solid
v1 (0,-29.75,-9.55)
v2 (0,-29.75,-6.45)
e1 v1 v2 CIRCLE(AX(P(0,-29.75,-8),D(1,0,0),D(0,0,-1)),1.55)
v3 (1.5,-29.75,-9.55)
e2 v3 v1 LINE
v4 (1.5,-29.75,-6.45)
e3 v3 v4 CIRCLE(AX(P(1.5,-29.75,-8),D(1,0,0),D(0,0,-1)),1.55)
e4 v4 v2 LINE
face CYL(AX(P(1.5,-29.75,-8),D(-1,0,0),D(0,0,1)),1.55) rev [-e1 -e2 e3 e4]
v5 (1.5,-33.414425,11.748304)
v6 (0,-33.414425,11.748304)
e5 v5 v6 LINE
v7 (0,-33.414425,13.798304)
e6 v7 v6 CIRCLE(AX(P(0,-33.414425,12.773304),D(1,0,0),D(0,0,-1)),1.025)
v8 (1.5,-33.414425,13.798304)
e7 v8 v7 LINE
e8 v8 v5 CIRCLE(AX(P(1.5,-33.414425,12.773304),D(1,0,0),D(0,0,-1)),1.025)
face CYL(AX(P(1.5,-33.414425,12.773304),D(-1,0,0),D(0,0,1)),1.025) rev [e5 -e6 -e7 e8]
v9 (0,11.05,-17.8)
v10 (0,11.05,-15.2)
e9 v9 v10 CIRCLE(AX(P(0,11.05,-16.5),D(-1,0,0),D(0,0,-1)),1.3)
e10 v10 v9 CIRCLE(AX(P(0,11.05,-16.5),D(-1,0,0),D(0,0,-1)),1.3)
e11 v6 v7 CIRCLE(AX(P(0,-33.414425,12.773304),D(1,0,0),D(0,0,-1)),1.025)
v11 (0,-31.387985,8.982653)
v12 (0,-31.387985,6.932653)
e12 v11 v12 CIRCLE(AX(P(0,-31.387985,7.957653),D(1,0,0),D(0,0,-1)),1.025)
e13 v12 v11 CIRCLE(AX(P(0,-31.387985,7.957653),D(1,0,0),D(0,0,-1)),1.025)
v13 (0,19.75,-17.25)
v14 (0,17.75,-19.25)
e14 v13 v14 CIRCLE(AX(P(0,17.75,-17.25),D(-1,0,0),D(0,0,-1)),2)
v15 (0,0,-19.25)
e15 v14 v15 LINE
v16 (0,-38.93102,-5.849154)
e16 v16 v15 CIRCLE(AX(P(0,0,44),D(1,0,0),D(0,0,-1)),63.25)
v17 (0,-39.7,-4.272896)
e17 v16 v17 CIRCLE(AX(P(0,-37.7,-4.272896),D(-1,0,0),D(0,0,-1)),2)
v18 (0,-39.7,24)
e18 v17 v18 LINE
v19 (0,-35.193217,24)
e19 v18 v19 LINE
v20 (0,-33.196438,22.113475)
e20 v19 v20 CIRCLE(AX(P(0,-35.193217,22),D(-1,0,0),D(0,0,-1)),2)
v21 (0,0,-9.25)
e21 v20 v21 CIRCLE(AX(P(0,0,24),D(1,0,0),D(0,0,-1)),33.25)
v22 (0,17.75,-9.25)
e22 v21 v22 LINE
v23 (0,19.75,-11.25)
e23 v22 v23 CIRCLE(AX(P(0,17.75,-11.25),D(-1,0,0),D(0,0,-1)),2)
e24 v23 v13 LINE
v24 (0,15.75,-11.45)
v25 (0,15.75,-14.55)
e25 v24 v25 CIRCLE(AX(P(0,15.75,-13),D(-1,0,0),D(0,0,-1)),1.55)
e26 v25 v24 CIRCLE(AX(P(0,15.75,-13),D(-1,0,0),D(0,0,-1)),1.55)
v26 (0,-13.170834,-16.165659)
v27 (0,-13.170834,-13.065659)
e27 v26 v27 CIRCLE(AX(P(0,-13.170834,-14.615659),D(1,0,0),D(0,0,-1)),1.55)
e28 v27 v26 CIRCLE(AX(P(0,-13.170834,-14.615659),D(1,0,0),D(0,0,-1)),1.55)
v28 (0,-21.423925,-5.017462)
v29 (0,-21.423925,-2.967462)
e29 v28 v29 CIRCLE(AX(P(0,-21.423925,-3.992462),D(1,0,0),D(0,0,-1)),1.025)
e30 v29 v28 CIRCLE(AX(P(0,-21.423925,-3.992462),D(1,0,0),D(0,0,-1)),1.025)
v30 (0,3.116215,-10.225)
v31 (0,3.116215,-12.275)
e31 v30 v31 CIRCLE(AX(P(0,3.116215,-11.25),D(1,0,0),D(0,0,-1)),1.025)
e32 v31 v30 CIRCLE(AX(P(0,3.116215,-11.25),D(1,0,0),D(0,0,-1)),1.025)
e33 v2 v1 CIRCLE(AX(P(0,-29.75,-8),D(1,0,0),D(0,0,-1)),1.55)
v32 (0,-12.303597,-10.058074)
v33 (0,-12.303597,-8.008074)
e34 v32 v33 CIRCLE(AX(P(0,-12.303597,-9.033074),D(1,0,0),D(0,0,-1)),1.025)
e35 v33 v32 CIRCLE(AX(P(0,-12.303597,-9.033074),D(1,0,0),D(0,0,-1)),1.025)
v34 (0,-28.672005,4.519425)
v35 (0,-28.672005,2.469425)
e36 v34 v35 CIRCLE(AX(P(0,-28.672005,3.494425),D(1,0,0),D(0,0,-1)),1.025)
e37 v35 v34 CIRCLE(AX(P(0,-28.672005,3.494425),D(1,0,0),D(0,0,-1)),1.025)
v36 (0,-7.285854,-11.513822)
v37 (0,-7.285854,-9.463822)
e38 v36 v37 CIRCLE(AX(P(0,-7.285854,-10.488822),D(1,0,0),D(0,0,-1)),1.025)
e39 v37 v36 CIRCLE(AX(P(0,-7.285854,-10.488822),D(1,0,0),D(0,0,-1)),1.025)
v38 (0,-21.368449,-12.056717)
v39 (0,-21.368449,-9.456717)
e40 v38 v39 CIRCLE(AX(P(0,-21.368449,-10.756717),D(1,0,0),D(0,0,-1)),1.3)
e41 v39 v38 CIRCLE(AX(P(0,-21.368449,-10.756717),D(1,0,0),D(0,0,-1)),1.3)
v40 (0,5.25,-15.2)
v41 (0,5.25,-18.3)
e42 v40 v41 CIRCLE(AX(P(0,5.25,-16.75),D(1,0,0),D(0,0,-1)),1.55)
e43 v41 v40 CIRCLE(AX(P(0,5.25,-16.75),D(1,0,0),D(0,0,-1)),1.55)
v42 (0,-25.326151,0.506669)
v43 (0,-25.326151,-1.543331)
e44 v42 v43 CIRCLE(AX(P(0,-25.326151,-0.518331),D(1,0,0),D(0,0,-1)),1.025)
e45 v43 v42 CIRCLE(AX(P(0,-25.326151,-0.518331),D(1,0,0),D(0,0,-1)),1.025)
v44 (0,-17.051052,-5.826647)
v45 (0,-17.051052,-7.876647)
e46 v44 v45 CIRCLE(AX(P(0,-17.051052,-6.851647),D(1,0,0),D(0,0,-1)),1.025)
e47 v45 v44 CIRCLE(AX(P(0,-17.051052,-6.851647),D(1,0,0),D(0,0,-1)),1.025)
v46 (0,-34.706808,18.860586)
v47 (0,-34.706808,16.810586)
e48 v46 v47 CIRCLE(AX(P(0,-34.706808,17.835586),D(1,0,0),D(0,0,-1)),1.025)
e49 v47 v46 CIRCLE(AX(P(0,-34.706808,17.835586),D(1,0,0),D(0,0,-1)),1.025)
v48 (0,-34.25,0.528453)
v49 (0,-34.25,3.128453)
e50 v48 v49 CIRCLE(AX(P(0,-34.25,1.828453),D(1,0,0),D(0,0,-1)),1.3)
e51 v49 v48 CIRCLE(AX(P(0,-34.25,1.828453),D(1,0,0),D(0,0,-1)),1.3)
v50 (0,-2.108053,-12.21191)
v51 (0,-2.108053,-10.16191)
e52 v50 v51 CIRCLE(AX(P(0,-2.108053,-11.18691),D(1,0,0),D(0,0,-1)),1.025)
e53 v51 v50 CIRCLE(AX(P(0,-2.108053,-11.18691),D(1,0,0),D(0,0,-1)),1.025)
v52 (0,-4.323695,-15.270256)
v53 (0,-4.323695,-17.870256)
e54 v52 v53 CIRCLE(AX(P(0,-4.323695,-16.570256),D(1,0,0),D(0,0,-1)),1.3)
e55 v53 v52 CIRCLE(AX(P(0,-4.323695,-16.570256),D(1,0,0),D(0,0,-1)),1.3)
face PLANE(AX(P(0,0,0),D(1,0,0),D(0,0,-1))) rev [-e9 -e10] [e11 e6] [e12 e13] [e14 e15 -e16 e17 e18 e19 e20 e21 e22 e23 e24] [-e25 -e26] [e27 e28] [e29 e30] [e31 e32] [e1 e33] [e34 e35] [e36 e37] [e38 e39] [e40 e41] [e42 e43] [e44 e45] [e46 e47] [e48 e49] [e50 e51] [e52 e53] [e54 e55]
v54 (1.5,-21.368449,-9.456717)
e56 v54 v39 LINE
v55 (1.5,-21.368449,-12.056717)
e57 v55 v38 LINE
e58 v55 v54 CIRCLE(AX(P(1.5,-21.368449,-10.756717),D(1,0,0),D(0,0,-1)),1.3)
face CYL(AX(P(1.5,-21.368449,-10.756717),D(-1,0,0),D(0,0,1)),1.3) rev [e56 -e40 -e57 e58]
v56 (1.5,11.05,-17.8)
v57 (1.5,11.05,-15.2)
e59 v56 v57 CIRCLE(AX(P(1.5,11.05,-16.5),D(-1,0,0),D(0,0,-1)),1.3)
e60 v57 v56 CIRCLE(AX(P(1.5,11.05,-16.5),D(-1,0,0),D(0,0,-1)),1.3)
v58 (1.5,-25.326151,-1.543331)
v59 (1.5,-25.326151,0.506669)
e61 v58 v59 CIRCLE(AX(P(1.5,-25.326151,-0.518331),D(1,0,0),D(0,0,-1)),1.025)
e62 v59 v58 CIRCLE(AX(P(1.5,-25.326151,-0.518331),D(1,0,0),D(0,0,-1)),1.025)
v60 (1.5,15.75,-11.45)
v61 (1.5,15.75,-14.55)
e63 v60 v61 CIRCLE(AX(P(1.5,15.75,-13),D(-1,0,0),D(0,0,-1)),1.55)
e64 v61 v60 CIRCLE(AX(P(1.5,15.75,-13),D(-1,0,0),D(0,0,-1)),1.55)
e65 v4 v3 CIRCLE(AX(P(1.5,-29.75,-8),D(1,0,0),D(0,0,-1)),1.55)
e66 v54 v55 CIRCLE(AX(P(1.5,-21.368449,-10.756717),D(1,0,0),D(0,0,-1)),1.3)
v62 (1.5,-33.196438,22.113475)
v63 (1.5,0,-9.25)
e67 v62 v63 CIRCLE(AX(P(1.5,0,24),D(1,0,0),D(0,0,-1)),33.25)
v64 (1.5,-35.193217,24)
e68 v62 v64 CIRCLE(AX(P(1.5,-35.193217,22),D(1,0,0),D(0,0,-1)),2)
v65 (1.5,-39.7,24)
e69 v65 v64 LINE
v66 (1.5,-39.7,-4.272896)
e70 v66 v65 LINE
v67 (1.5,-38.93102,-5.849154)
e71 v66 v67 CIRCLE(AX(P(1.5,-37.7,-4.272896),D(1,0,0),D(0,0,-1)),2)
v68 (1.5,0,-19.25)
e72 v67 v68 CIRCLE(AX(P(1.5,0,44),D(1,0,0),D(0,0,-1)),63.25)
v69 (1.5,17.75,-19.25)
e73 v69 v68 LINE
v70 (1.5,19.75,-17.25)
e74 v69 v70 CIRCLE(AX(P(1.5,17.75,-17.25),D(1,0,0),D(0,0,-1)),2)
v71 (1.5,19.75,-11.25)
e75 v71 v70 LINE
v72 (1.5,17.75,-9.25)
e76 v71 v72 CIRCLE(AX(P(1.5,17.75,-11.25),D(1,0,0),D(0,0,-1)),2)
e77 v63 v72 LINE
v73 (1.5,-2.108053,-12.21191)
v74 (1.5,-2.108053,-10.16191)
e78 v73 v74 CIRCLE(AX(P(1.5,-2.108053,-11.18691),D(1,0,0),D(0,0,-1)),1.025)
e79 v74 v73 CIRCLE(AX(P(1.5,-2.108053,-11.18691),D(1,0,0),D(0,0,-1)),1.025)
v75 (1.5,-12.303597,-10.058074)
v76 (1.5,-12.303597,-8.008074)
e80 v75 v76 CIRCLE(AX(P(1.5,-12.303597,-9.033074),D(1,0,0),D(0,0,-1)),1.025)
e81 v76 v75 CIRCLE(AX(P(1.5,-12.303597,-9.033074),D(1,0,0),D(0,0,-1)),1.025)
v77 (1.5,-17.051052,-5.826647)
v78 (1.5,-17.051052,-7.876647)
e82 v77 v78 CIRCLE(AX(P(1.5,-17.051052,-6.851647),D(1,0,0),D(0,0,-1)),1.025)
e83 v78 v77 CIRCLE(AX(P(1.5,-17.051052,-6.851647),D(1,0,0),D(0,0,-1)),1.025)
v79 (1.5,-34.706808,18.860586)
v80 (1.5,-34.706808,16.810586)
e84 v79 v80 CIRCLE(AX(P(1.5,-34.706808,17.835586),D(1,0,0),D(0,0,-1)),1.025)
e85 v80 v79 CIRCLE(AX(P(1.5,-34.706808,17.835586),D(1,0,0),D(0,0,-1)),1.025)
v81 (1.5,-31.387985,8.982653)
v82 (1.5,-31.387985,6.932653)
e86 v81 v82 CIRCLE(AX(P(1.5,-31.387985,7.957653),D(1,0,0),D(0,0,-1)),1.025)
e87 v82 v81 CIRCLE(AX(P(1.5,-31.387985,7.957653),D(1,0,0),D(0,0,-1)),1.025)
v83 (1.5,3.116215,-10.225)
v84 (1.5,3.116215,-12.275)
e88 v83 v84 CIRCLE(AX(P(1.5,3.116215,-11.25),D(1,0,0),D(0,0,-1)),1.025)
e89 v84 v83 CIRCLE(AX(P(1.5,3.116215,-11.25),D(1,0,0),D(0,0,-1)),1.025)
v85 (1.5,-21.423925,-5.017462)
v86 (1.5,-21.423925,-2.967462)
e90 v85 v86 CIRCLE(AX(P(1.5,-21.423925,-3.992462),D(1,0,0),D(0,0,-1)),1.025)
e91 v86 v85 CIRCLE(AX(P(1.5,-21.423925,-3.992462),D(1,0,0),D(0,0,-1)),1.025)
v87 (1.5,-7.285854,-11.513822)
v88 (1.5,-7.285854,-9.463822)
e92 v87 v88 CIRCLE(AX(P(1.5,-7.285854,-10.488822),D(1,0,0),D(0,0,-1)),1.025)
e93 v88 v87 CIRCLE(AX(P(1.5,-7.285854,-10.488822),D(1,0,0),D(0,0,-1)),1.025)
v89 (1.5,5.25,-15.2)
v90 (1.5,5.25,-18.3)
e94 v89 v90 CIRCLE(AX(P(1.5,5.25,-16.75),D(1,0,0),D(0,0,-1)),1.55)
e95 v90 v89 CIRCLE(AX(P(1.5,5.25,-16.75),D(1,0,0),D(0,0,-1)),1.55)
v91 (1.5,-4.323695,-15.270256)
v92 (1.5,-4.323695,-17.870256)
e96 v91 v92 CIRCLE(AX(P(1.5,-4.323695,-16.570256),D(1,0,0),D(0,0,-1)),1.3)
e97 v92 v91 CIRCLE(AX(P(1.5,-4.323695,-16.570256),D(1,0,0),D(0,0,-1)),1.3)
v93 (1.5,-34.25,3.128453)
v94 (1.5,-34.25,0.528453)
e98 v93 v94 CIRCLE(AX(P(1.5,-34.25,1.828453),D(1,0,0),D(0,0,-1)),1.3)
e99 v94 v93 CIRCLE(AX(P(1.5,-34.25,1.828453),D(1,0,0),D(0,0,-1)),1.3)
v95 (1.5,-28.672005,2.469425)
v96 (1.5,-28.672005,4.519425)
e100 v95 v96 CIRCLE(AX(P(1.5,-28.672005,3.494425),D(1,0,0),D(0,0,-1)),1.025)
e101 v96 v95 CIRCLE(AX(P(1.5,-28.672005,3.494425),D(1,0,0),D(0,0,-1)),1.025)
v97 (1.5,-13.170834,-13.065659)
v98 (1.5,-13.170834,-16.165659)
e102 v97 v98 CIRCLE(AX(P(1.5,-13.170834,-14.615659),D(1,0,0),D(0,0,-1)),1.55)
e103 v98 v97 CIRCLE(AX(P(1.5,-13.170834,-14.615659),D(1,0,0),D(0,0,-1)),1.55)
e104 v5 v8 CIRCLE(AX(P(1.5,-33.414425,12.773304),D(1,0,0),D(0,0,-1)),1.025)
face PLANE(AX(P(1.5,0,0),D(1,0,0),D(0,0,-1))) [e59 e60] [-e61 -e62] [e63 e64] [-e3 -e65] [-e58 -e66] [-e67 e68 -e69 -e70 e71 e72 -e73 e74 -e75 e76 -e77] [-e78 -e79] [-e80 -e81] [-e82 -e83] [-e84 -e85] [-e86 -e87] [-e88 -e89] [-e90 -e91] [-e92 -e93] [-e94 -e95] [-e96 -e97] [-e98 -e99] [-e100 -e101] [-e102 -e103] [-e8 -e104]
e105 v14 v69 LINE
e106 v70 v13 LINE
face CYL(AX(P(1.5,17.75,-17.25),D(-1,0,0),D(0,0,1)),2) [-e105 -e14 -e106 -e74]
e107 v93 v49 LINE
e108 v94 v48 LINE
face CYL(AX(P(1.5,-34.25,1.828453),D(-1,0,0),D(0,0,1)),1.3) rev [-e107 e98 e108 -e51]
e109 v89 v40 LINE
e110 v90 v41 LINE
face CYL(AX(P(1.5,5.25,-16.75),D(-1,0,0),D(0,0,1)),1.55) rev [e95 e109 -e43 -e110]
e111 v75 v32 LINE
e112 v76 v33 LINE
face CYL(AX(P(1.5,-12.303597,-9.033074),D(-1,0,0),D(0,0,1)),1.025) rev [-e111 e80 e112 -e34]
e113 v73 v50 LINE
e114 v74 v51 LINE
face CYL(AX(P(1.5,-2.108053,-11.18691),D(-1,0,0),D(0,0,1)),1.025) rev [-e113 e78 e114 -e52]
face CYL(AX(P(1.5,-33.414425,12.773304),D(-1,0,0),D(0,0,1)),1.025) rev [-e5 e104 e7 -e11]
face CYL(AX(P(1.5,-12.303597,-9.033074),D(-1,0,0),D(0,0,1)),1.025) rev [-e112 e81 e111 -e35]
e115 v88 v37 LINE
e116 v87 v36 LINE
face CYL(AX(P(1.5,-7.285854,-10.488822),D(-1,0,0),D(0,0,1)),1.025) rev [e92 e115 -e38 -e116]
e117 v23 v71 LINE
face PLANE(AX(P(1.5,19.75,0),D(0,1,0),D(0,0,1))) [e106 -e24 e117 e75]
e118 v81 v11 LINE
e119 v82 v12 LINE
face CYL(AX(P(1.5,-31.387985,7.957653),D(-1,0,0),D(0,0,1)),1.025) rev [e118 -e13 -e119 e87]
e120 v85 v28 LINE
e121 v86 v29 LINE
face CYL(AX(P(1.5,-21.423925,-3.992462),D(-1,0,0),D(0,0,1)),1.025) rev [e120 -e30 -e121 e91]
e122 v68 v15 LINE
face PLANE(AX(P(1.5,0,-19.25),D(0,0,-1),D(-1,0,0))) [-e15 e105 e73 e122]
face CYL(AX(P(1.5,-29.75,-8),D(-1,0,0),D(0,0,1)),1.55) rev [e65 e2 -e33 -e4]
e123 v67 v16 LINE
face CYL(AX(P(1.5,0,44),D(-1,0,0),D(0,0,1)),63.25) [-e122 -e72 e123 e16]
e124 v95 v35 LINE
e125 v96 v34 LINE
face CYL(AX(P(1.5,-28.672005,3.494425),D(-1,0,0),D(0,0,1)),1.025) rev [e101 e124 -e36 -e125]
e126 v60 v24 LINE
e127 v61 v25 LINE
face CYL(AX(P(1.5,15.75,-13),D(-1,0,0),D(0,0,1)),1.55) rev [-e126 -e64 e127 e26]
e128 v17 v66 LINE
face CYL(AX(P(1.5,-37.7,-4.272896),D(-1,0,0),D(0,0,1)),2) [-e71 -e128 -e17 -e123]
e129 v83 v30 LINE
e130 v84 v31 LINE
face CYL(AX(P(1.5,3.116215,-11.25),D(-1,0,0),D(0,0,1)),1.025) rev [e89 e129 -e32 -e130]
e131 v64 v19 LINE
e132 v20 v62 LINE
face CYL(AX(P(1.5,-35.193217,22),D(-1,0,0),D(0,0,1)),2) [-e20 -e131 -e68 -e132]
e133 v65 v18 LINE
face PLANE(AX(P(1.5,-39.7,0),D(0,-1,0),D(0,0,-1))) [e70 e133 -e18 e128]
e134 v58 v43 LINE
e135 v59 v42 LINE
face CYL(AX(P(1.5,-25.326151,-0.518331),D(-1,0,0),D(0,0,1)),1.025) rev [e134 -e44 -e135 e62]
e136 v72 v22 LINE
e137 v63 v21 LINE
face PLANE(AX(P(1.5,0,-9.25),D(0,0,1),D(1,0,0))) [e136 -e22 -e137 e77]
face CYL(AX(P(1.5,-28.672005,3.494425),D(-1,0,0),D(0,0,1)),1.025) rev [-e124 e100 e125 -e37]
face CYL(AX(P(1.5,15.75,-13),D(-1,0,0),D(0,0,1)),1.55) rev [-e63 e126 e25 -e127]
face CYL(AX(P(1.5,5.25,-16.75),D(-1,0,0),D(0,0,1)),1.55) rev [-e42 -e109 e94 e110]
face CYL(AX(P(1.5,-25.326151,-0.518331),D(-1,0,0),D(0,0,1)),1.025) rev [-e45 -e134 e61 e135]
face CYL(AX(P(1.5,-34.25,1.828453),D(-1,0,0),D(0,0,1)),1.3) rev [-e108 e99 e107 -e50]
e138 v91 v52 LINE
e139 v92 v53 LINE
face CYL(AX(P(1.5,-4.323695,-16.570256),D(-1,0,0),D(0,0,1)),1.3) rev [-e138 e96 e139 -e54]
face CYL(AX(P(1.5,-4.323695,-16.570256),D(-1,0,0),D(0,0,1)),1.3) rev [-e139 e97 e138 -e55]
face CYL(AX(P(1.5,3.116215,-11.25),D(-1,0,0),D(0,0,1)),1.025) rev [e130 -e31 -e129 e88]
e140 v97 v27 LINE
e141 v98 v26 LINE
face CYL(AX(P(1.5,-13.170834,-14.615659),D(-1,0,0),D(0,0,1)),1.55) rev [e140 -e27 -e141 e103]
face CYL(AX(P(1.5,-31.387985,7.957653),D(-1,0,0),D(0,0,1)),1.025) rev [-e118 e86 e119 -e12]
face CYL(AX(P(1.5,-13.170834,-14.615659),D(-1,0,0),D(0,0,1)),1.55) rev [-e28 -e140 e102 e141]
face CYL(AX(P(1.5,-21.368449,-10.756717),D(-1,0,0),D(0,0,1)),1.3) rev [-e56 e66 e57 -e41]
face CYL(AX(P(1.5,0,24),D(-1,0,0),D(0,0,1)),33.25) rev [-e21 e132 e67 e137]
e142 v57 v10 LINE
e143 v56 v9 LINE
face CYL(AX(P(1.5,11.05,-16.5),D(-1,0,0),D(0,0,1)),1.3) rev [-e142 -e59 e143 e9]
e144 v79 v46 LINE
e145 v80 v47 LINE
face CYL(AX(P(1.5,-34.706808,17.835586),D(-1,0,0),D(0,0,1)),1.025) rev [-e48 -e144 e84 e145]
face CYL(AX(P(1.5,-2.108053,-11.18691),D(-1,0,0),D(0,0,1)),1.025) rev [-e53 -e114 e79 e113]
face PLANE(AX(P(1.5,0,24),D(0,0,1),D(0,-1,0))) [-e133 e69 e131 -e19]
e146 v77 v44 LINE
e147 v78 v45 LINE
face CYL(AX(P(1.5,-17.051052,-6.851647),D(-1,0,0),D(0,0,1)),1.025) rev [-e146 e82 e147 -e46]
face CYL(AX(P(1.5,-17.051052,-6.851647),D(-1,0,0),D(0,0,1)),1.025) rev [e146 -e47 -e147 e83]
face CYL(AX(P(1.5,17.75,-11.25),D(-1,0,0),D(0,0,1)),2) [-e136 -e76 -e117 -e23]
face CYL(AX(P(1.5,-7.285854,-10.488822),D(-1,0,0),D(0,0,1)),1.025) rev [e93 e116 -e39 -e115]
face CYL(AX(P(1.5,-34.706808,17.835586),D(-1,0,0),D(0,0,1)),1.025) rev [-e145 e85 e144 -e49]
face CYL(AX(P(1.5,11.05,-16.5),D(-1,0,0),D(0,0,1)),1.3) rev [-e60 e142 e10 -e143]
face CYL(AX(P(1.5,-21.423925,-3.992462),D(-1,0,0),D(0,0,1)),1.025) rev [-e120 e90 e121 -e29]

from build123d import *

# Parameters (mm, degrees)
SKETCH_1_R      = 1.55
SKETCH_1_R_2    = 1.025
SKETCH_1_R_3    = 1.3
EXTRUDE_1_DEPTH = 1.5
FILLET_R2_1_R   = 2


with BuildPart() as part:
    # 草图1 → 凸台-拉伸1 (new body)
    with BuildSketch(Plane(origin=(0, 0, 0), x_dir=(0, 0, -1), z_dir=(1, 0, 0))):
        with BuildLine():
            Line((9.25, 19.75), (9.25, 0))
            ThreePointArc((9.25, 0), (-0.488699526, -23.511300474), (-24, -33.25))
            Line((-24, -33.25), (-24, -39.7))
            Line((-24, -39.7), (5.238932767, -39.7))
            ThreePointArc((5.238932767, -39.7), (15.644467461, -21.049940647), (19.25, 0))
            Line((19.25, 0), (19.25, 19.75))
            Line((19.25, 19.75), (9.25, 19.75))
        make_face()
        with Locations((13, 15.75)):
            Circle(SKETCH_1_R, mode=Mode.SUBTRACT)
        with Locations((11.25, 3.116215025)):
            Circle(SKETCH_1_R_2, mode=Mode.SUBTRACT)
        with Locations((-17.835585997, -34.70680769)):
            Circle(SKETCH_1_R_2, mode=Mode.SUBTRACT)
        with Locations((-12.773303956, -33.414424968)):
            Circle(SKETCH_1_R_2, mode=Mode.SUBTRACT)
        with Locations((-7.957653042, -31.387985027)):
            Circle(SKETCH_1_R_2, mode=Mode.SUBTRACT)
        with Locations((-3.494424789, -28.672005254)):
            Circle(SKETCH_1_R_2, mode=Mode.SUBTRACT)
        with Locations((0.518331383, -25.326151034)):
            Circle(SKETCH_1_R_2, mode=Mode.SUBTRACT)
        with Locations((3.992462152, -21.423925006)):
            Circle(SKETCH_1_R_2, mode=Mode.SUBTRACT)
        with Locations((6.851646862, -17.05105234)):
            Circle(SKETCH_1_R_2, mode=Mode.SUBTRACT)
        with Locations((9.033074163, -12.303597496)):
            Circle(SKETCH_1_R_2, mode=Mode.SUBTRACT)
        with Locations((10.488821863, -7.285853861)):
            Circle(SKETCH_1_R_2, mode=Mode.SUBTRACT)
        with Locations((11.1869097, -2.108052596)):
            Circle(SKETCH_1_R_2, mode=Mode.SUBTRACT)
        with Locations((16.57025586, -4.32369512)):
            Circle(SKETCH_1_R_3, mode=Mode.SUBTRACT)
        with Locations((14.615659071, -13.170834237)):
            Circle(SKETCH_1_R, mode=Mode.SUBTRACT)
        with Locations((16.5, 11.05)):
            Circle(SKETCH_1_R_3, mode=Mode.SUBTRACT)
        with Locations((16.75, 5.25)):
            Circle(SKETCH_1_R, mode=Mode.SUBTRACT)
        with Locations((-1.828452918, -34.25)):
            Circle(SKETCH_1_R_3, mode=Mode.SUBTRACT)
        with Locations((8, -29.75)):
            Circle(SKETCH_1_R, mode=Mode.SUBTRACT)
        with Locations((10.756717193, -21.368448937)):
            Circle(SKETCH_1_R_3, mode=Mode.SUBTRACT)
    extrude(amount=EXTRUDE_1_DEPTH)

    # R2 圆角1
    fillet_r2_1_edges = [part.edges().sort_by_distance(p)[0] for p in [
        (0.75, 19.75, -19.25),
        (0.75, -39.7, -5.238932767),
        (0.75, -33.25, 24),
        (0.75, 19.75, -9.25),
    ]]
    fillet(fillet_r2_1_edges, radius=FILLET_R2_1_R)


solid = part.part
